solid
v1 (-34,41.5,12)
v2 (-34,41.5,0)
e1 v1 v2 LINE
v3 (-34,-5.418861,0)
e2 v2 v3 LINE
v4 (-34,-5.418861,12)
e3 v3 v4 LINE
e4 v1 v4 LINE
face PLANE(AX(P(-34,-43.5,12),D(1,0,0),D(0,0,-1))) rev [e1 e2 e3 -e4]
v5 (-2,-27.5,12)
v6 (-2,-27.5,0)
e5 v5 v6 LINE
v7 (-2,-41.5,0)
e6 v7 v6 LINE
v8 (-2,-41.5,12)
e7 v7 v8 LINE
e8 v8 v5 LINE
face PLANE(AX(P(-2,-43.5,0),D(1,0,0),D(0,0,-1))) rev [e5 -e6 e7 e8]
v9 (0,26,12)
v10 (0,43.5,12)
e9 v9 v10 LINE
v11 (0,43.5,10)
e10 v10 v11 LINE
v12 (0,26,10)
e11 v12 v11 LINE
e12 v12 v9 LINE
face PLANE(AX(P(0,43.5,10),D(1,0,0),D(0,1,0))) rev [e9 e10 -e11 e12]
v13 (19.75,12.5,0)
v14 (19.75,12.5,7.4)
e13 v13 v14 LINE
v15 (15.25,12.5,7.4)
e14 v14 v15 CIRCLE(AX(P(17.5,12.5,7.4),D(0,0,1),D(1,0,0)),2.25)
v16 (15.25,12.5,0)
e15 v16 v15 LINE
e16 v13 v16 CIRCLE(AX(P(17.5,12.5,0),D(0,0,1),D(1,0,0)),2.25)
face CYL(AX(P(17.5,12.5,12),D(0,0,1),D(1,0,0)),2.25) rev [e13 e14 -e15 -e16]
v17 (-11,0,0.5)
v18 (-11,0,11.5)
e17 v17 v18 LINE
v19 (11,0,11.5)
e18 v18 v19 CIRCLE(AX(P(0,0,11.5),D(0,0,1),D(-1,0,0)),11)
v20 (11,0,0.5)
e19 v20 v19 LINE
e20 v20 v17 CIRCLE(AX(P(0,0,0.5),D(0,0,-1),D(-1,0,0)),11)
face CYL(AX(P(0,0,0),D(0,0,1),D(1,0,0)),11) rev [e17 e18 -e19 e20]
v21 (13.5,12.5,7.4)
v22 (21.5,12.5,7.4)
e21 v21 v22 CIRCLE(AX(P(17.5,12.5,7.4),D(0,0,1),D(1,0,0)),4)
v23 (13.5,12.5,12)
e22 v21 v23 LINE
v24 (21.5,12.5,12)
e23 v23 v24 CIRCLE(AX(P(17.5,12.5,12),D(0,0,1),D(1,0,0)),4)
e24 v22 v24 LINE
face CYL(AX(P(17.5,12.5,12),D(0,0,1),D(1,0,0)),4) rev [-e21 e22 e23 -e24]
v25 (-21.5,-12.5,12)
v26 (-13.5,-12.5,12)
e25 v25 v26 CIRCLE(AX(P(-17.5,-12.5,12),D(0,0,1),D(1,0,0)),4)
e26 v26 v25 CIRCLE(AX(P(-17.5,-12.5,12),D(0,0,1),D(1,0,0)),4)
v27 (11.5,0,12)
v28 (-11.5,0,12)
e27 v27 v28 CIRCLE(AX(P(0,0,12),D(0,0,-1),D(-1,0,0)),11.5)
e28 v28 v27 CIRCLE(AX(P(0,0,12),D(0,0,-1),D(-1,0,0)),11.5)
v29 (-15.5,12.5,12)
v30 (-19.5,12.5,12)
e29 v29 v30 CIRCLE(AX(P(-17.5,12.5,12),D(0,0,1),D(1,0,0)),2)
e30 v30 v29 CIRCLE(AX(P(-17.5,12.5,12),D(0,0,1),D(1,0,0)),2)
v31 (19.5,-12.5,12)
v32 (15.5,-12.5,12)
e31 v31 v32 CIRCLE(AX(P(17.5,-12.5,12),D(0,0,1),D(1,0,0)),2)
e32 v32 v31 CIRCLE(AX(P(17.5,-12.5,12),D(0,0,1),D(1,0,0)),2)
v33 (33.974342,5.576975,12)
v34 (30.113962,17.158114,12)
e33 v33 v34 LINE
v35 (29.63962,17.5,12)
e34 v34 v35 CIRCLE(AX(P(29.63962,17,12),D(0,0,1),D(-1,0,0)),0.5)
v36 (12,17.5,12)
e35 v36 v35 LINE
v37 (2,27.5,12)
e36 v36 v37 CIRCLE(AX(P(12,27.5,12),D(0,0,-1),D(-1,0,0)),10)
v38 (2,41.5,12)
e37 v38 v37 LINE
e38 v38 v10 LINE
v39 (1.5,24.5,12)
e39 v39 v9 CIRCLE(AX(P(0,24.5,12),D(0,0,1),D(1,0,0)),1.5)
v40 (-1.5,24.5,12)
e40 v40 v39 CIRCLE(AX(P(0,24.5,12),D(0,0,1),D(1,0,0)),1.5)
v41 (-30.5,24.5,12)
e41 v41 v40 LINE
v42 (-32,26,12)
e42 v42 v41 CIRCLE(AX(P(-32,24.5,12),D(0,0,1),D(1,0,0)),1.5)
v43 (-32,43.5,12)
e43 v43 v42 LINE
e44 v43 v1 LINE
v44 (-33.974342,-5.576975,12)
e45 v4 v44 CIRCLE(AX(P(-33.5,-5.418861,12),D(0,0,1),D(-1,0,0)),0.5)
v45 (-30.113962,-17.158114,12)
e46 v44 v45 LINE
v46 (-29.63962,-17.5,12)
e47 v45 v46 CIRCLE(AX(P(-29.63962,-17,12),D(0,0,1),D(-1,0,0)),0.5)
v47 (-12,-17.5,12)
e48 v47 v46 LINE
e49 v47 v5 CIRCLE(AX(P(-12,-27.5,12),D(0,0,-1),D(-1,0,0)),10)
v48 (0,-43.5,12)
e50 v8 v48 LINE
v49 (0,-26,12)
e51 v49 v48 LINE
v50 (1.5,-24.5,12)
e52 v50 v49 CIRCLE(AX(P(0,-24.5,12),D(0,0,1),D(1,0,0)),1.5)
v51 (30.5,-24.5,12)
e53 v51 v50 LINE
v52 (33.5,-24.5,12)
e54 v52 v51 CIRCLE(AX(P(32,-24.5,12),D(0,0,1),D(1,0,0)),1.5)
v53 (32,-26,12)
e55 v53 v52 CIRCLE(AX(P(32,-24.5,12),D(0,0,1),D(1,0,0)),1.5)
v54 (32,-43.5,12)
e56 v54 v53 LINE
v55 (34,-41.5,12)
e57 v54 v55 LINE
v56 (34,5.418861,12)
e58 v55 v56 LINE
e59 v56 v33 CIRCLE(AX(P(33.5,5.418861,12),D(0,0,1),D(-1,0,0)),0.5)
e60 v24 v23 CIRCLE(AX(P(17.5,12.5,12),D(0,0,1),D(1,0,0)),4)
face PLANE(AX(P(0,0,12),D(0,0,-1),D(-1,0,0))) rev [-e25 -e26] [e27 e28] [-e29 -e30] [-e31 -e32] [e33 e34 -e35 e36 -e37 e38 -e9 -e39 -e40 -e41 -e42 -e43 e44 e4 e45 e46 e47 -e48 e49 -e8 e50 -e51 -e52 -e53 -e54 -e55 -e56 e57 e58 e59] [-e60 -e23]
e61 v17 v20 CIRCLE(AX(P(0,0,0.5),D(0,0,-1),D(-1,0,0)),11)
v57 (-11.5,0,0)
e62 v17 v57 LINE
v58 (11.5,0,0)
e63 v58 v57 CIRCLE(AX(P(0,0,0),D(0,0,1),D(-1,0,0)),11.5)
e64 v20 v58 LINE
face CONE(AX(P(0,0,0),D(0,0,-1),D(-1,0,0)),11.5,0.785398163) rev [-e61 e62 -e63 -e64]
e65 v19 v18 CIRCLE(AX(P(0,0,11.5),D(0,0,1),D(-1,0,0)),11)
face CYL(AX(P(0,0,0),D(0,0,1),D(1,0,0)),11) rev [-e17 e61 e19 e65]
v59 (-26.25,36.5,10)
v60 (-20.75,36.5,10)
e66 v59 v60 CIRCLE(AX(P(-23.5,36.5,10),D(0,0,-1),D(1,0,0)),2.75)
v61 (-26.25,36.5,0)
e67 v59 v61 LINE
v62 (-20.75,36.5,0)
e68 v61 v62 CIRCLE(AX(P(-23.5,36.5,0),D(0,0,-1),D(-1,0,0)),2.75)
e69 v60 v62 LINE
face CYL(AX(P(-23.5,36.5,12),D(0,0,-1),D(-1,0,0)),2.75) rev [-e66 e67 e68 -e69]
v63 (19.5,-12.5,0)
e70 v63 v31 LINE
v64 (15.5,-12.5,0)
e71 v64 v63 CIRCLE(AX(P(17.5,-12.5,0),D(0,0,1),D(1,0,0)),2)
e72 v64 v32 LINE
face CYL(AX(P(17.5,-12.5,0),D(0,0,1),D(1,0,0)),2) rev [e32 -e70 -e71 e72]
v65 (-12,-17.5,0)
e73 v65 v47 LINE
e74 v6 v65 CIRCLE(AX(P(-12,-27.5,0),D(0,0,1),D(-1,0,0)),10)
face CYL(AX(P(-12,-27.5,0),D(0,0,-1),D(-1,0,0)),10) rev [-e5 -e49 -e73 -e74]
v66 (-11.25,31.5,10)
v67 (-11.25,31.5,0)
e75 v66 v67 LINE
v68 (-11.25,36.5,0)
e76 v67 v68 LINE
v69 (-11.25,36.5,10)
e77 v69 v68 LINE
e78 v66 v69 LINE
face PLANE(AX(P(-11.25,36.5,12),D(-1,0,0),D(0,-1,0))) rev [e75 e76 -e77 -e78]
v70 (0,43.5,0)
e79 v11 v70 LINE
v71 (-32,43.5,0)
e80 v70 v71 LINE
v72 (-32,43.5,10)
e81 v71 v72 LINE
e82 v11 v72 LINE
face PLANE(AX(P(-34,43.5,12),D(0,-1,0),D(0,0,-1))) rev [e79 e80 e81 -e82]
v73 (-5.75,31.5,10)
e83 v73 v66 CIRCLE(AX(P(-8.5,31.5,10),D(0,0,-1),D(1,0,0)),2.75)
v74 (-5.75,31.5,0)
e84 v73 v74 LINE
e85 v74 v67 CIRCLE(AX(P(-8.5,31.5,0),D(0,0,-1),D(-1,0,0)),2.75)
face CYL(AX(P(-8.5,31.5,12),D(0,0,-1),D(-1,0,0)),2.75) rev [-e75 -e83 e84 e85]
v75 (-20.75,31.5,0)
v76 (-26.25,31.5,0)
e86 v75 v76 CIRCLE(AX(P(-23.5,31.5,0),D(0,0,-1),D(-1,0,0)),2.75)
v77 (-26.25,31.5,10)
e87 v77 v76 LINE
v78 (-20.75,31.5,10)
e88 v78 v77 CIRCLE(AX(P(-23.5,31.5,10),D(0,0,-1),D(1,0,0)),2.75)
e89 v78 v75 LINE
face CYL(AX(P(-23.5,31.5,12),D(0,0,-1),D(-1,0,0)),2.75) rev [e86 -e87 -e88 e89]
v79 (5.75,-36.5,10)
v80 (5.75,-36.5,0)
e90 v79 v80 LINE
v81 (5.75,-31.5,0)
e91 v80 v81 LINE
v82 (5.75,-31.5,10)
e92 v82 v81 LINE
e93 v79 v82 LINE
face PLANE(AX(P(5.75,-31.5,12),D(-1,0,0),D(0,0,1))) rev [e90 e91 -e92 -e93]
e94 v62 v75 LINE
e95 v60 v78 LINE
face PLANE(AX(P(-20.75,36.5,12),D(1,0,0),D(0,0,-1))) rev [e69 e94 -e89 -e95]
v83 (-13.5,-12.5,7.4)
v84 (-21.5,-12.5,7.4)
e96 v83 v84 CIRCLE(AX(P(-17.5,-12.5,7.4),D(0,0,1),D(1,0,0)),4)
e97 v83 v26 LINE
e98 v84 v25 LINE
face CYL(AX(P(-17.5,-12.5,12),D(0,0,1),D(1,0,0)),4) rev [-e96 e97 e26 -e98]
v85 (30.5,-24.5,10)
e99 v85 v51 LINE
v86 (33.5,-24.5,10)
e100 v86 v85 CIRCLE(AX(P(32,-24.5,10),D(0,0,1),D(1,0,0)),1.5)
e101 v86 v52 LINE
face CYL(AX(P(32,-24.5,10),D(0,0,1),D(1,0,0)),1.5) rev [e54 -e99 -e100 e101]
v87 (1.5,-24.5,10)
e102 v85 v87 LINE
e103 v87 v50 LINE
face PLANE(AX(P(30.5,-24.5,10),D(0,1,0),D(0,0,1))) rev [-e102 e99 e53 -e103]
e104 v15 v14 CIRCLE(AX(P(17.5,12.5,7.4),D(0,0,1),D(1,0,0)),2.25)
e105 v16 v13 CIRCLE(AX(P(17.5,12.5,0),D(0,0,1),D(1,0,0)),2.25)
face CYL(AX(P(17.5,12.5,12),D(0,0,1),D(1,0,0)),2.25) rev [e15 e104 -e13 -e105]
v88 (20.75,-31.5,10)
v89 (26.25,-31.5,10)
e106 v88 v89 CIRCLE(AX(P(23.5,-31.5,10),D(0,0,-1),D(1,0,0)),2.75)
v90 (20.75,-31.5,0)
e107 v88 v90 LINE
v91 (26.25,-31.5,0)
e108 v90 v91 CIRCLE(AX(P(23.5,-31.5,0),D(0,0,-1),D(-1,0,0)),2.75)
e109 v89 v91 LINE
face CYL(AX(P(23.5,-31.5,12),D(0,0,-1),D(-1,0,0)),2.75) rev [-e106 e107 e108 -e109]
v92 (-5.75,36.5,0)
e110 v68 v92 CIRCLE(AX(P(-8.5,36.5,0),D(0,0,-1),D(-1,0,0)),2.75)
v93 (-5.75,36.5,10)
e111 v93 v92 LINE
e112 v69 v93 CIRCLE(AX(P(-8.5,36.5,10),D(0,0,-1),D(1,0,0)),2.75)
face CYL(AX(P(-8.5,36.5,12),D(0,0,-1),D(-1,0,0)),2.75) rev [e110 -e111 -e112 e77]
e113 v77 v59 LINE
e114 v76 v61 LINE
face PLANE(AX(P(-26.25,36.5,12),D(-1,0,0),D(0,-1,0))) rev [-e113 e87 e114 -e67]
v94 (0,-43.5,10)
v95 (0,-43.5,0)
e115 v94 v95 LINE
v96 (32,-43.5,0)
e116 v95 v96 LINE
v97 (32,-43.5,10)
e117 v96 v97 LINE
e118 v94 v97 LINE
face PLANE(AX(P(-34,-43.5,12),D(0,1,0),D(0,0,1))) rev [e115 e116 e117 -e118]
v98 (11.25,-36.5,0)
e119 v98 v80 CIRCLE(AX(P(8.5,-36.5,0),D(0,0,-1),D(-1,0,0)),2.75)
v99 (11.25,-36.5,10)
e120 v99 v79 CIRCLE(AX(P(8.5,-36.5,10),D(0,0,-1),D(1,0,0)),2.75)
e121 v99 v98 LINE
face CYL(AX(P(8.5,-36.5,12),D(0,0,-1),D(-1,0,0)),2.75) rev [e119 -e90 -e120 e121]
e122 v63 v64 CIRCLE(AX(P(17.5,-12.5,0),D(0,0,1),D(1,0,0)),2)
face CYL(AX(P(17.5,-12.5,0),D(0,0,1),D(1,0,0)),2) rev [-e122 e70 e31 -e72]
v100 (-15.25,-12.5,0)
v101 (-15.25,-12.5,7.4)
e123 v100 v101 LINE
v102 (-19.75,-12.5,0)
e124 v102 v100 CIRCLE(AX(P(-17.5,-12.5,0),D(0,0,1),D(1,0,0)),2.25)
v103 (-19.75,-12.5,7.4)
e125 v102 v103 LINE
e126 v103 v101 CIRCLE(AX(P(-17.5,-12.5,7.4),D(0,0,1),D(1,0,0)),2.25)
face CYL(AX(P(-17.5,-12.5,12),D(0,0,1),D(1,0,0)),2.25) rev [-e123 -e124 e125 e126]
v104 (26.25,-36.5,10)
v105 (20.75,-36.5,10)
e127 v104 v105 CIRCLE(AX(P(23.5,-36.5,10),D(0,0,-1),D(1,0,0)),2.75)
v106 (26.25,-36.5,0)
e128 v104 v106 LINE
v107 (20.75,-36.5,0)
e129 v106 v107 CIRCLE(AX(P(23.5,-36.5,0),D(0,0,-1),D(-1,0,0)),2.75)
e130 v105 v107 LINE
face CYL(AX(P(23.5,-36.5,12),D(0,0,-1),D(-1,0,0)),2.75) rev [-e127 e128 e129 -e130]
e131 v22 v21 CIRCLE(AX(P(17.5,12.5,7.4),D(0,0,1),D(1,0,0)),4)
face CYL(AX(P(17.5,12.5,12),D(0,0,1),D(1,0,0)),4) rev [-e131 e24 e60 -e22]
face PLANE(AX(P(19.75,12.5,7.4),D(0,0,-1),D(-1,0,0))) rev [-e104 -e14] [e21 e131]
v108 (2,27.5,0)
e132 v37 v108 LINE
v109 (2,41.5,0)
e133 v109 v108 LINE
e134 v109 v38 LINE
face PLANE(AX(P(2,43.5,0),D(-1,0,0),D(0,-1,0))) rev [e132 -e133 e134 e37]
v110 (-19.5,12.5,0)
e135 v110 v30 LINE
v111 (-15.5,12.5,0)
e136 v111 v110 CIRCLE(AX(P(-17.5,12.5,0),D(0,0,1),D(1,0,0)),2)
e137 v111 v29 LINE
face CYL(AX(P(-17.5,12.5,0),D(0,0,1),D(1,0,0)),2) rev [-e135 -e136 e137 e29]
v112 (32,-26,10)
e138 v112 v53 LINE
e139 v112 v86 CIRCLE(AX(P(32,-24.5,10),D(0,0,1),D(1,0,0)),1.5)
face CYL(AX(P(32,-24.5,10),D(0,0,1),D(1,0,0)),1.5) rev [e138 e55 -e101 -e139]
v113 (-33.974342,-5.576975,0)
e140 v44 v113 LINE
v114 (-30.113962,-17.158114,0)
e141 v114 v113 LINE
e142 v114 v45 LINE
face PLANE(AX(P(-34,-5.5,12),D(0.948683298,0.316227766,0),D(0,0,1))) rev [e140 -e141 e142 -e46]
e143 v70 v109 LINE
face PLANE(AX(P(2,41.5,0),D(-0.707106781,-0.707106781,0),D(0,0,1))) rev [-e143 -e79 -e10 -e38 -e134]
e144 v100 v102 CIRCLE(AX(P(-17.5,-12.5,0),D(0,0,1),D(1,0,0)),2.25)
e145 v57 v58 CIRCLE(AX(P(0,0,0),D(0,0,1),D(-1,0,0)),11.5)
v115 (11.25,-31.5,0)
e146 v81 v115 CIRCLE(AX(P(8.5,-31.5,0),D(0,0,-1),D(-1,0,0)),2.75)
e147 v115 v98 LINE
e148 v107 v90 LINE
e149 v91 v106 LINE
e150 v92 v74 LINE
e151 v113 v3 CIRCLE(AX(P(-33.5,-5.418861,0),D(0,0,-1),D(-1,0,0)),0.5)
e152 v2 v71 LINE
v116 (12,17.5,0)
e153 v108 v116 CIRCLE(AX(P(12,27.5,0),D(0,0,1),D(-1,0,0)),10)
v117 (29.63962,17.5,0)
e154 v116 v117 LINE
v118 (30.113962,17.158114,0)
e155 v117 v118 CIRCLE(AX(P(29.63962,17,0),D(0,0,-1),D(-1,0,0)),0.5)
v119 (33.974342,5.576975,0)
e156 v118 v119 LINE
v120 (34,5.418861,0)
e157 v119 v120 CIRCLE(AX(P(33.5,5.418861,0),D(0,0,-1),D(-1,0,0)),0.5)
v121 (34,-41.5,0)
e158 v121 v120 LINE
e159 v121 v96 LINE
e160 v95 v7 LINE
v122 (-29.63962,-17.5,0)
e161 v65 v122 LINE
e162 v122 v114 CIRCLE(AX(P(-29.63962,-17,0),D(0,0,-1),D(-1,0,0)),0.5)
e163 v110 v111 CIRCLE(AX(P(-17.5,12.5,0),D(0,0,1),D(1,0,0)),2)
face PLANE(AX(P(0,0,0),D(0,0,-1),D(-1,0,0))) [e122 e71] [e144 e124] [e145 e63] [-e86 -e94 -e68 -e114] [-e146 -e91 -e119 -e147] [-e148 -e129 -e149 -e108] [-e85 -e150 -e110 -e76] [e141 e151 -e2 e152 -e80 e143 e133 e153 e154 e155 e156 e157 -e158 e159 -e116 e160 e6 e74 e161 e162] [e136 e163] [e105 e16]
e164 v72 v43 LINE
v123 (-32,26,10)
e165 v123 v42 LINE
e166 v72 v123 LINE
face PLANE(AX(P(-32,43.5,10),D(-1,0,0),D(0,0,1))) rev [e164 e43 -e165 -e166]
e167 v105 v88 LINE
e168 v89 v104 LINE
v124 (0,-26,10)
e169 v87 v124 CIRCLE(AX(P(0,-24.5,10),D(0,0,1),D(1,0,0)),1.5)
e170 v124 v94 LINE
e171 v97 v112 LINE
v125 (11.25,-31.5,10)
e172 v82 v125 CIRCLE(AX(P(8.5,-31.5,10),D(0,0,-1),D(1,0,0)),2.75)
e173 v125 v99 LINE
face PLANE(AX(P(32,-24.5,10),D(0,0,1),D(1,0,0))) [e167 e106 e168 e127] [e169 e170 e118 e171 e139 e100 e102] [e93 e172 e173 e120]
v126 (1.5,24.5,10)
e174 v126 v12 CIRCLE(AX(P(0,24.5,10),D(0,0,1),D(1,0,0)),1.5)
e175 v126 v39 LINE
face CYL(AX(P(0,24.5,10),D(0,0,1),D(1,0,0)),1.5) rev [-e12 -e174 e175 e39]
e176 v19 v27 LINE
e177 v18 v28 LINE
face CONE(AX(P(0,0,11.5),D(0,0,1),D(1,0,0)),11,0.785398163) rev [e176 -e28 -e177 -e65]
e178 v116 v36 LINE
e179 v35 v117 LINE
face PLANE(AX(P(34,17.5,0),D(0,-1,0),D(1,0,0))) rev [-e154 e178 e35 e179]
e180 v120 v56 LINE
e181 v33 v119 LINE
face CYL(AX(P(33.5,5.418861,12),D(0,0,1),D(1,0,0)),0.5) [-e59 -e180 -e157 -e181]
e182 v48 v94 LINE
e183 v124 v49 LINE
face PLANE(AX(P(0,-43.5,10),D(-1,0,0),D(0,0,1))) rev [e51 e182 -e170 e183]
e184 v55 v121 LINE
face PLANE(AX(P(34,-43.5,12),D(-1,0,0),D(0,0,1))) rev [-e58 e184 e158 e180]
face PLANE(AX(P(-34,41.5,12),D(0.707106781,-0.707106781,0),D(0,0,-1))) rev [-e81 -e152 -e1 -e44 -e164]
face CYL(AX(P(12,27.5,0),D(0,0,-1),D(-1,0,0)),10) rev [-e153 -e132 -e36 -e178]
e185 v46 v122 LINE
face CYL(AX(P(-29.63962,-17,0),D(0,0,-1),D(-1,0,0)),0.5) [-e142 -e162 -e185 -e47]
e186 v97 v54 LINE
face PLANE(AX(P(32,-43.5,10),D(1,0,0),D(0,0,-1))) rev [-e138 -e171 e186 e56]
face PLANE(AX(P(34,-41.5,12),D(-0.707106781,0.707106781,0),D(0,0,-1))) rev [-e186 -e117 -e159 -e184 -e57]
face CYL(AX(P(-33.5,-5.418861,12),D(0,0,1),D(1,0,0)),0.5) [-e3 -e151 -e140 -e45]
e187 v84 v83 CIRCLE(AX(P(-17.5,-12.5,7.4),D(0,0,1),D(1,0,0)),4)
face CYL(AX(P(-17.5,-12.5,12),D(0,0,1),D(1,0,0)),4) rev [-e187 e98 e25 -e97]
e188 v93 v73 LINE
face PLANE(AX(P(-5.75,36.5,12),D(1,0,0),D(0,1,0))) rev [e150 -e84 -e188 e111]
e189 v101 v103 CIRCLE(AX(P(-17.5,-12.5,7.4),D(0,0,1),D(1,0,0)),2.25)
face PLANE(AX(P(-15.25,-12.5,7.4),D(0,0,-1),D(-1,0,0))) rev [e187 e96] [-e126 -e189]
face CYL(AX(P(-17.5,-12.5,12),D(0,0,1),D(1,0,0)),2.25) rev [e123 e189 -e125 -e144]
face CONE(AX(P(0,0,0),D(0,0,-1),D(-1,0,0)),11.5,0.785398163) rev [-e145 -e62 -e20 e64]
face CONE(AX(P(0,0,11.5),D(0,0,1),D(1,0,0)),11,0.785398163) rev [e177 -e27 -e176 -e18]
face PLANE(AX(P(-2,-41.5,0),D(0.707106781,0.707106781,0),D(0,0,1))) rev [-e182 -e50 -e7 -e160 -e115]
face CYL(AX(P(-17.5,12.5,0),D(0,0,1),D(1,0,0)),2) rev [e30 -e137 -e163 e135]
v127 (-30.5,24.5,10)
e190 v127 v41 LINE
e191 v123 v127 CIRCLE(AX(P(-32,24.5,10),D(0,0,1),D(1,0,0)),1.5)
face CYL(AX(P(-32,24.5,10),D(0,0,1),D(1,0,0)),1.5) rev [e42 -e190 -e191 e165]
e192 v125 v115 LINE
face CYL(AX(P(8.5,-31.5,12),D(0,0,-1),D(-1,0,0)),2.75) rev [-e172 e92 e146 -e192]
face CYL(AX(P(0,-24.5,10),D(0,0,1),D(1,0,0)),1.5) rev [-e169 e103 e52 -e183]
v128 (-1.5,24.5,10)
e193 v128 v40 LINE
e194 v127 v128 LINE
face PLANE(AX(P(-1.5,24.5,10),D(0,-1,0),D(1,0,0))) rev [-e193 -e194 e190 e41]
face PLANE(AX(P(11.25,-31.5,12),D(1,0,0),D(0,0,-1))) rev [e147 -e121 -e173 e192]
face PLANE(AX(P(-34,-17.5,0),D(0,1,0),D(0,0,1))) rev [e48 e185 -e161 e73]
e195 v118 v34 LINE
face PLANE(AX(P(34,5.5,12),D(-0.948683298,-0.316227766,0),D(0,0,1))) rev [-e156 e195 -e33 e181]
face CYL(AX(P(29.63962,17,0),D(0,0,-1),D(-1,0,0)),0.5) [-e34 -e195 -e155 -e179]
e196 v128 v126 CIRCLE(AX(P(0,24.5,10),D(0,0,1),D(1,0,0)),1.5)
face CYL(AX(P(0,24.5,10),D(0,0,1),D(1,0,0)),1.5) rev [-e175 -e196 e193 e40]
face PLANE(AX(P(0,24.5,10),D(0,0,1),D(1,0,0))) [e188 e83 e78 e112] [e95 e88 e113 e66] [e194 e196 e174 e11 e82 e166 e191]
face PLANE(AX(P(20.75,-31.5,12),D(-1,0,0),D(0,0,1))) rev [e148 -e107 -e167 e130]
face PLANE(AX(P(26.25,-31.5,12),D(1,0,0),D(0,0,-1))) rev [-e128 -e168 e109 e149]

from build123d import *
from OCP.BRepFilletAPI import BRepFilletAPI_MakeChamfer

# Parameters (mm, degrees)
SKETCH1_W                                            = 68
SKETCH1_H                                            = 87
BOSS_EXTRUDE1_DEPTH                                  = 12
SKETCH3_R                                            = 11
SKETCH3_R_2                                          = 2
SKETCH3_W                                            = 32
SKETCH3_H                                            = 26
CUT_EXTRUDE2_DEPTH                                   = 57.5
FILLET1_R                                            = 10
CHAMFER1_SIZE                                        = 2
CHAMFER2_SIZE                                        = 4
CHAMFER2_SIZE2                                       = 12
FILLET3_R                                            = 0.5
CUT_EXTRUDE4_DEPTH                                   = 57.5
HOLE_SIZE_BY_SOCKET_HEAD_CAP_SCREW_TYPE0_D           = 4.5
HOLE_SIZE_BY_SOCKET_HEAD_CAP_SCREW_TYPE0_CBORE_D     = 8
HOLE_SIZE_BY_SOCKET_HEAD_CAP_SCREW_TYPE0_CBORE_DEPTH = 4.6
CHAMFER3_SIZE                                        = 0.5
CUT_EXTRUDE3_DEPTH                                   = 2


with BuildPart() as part:
    # Sketch1 → Boss-Extrude1 (new body)
    with BuildSketch(Plane.XY):
        Rectangle(SKETCH1_W, SKETCH1_H)
    extrude(amount=BOSS_EXTRUDE1_DEPTH)

    # Sketch3 → Cut-Extrude2 (cut, through all)
    with BuildSketch(Plane.XY.offset(12)):
        Circle(SKETCH3_R)
        with Locations((17.5, -12.5)):
            Circle(SKETCH3_R_2)
        with Locations((-17.5, 12.5)):
            Circle(SKETCH3_R_2)
        with Locations((18, 30.5)):
            Rectangle(SKETCH3_W, SKETCH3_H)
        with Locations((-18, -30.5)):
            Rectangle(SKETCH3_W, SKETCH3_H)
    extrude(amount=-CUT_EXTRUDE2_DEPTH, mode=Mode.SUBTRACT)

    # Fillet1
    fillet1_edges = [part.edges().sort_by_distance(p)[0] for p in [
        (2, 17.5, 6),
        (-2, -17.5, 6),
    ]]
    fillet(fillet1_edges, radius=FILLET1_R)

    # Chamfer1
    chamfer1_edges = [part.edges().sort_by_distance(p)[0] for p in [
        (2, 43.5, 6),
        (-2, -43.5, 6),
        (34, -43.5, 6),
        (-34, 43.5, 6),
    ]]
    chamfer(chamfer1_edges, length=CHAMFER1_SIZE)

    # Chamfer2: one chamfer whose edges measure the first distance from different faces: ONE call of the kernel's chamfer builder (chamfer() names one face for all edges)
    chamfer2_edges_1 = [part.edges().sort_by_distance(p)[0] for p in [
        (34, 17.5, 6),
    ]]
    chamfer2_side_1 = [part.faces().sort_by_distance(p)[0] for p in [
        (23, 17.5, 6),
    ]]
    chamfer2_edges_2 = [part.edges().sort_by_distance(p)[0] for p in [
        (-34, -17.5, 6),
    ]]
    chamfer2_side_2 = [part.faces().sort_by_distance(p)[0] for p in [
        (-23, -17.5, 6),
    ]]
    chamfer2 = BRepFilletAPI_MakeChamfer(part.part.solid().wrapped)
    for e in chamfer2_edges_1:
        chamfer2.Add(CHAMFER2_SIZE, CHAMFER2_SIZE2, e.wrapped, chamfer2_side_1[0].wrapped)  # the first distance lies on this face
    for e in chamfer2_edges_2:
        chamfer2.Add(CHAMFER2_SIZE, CHAMFER2_SIZE2, e.wrapped, chamfer2_side_2[0].wrapped)  # the first distance lies on this face
    add(Compound.cast(chamfer2.Shape()), mode=Mode.REPLACE)

    # Fillet3
    fillet3_edges = [part.edges().sort_by_distance(p)[0] for p in [
        (-34, -5.5, 6),
        (-30, -17.5, 6),
        (34, 5.5, 6),
        (30, 17.5, 6),
    ]]
    fillet(fillet3_edges, radius=FILLET3_R)

    # Sketch21 → Cut-Extrude4 (cut, through all)
    with BuildSketch(Plane(origin=(0, 0, 0), x_dir=(-1, 0, 0), z_dir=(0, 0, -1))):
        with BuildLine():
            Line((11.25, 36.5), (11.25, 31.500000357))
            ThreePointArc((11.25, 31.500000357), (8.5, 28.750000357), (5.75, 31.500000357))
            Line((5.75, 31.500000357), (5.75, 36.5))
            ThreePointArc((5.75, 36.5), (8.5, 39.25), (11.25, 36.5))
        make_face()
        with BuildLine():
            Line((26.25, 36.500000178), (26.25, 31.500000178))
            ThreePointArc((26.25, 31.500000178), (23.5, 28.750000357), (20.75, 31.500000178))
            Line((20.75, 31.500000178), (20.75, 36.500000178))
            ThreePointArc((20.75, 36.500000178), (23.5, 39.25), (26.25, 36.500000178))
        make_face()
        with BuildLine():
            Line((-20.75, -31.500000357), (-20.75, -36.5))
            ThreePointArc((-20.75, -36.5), (-23.5, -39.25), (-26.25, -36.5))
            Line((-26.25, -36.5), (-26.25, -31.500000357))
            ThreePointArc((-26.25, -31.500000357), (-23.5, -28.750000357), (-20.75, -31.500000357))
        make_face()
        with BuildLine():
            Line((-5.75, -31.500000357), (-5.75, -36.5))
            ThreePointArc((-5.75, -36.5), (-8.5, -39.25), (-11.25, -36.5))
            Line((-11.25, -36.5), (-11.25, -31.500000357))
            ThreePointArc((-11.25, -31.500000357), (-8.5, -28.750000357), (-5.75, -31.500000357))
        make_face()
    extrude(amount=-CUT_EXTRUDE4_DEPTH, mode=Mode.SUBTRACT)

    # Hole size by socket head cap screw type0 (through all)
    with Locations(Plane.XY.offset(12)):
        with Locations((17.5, 12.5), (-17.5, -12.5)):
            CounterBoreHole(HOLE_SIZE_BY_SOCKET_HEAD_CAP_SCREW_TYPE0_D / 2, HOLE_SIZE_BY_SOCKET_HEAD_CAP_SCREW_TYPE0_CBORE_D / 2, HOLE_SIZE_BY_SOCKET_HEAD_CAP_SCREW_TYPE0_CBORE_DEPTH)

    # Chamfer3
    chamfer3_edges = [part.edges().sort_by_distance(p)[0] for p in [
        (-11, 0, 0),
        (-11, 0, 12),
    ]]
    chamfer(chamfer3_edges, length=CHAMFER3_SIZE)

    # Sketch19 → Cut-Extrude3 (cut)
    with BuildSketch(Plane.XY.offset(12)):
        with BuildLine():
            Line((32, -43.5), (0, -43.5))
            Line((0, -43.5), (0, -26))
            ThreePointArc((0, -26), (-1.060660172, -23.439339828), (1.5, -24.5))
            Line((1.5, -24.5), (30.5, -24.5))
            ThreePointArc((30.5, -24.5), (33.060660172, -23.439339828), (32, -26))
            Line((32, -26), (32, -43.5))
        make_face()
        with BuildLine():
            Line((0, 43.5), (-32, 43.5))
            Line((-32, 43.5), (-32, 26))
            ThreePointArc((-32, 26), (-33.060660172, 23.439339828), (-30.5, 24.5))
            Line((-30.5, 24.5), (-1.5, 24.5))
            ThreePointArc((-1.5, 24.5), (1.060660172, 23.439339828), (0, 26))
            Line((0, 26), (0, 43.5))
        make_face()
    extrude(amount=-CUT_EXTRUDE3_DEPTH, mode=Mode.SUBTRACT)


solid = part.part
